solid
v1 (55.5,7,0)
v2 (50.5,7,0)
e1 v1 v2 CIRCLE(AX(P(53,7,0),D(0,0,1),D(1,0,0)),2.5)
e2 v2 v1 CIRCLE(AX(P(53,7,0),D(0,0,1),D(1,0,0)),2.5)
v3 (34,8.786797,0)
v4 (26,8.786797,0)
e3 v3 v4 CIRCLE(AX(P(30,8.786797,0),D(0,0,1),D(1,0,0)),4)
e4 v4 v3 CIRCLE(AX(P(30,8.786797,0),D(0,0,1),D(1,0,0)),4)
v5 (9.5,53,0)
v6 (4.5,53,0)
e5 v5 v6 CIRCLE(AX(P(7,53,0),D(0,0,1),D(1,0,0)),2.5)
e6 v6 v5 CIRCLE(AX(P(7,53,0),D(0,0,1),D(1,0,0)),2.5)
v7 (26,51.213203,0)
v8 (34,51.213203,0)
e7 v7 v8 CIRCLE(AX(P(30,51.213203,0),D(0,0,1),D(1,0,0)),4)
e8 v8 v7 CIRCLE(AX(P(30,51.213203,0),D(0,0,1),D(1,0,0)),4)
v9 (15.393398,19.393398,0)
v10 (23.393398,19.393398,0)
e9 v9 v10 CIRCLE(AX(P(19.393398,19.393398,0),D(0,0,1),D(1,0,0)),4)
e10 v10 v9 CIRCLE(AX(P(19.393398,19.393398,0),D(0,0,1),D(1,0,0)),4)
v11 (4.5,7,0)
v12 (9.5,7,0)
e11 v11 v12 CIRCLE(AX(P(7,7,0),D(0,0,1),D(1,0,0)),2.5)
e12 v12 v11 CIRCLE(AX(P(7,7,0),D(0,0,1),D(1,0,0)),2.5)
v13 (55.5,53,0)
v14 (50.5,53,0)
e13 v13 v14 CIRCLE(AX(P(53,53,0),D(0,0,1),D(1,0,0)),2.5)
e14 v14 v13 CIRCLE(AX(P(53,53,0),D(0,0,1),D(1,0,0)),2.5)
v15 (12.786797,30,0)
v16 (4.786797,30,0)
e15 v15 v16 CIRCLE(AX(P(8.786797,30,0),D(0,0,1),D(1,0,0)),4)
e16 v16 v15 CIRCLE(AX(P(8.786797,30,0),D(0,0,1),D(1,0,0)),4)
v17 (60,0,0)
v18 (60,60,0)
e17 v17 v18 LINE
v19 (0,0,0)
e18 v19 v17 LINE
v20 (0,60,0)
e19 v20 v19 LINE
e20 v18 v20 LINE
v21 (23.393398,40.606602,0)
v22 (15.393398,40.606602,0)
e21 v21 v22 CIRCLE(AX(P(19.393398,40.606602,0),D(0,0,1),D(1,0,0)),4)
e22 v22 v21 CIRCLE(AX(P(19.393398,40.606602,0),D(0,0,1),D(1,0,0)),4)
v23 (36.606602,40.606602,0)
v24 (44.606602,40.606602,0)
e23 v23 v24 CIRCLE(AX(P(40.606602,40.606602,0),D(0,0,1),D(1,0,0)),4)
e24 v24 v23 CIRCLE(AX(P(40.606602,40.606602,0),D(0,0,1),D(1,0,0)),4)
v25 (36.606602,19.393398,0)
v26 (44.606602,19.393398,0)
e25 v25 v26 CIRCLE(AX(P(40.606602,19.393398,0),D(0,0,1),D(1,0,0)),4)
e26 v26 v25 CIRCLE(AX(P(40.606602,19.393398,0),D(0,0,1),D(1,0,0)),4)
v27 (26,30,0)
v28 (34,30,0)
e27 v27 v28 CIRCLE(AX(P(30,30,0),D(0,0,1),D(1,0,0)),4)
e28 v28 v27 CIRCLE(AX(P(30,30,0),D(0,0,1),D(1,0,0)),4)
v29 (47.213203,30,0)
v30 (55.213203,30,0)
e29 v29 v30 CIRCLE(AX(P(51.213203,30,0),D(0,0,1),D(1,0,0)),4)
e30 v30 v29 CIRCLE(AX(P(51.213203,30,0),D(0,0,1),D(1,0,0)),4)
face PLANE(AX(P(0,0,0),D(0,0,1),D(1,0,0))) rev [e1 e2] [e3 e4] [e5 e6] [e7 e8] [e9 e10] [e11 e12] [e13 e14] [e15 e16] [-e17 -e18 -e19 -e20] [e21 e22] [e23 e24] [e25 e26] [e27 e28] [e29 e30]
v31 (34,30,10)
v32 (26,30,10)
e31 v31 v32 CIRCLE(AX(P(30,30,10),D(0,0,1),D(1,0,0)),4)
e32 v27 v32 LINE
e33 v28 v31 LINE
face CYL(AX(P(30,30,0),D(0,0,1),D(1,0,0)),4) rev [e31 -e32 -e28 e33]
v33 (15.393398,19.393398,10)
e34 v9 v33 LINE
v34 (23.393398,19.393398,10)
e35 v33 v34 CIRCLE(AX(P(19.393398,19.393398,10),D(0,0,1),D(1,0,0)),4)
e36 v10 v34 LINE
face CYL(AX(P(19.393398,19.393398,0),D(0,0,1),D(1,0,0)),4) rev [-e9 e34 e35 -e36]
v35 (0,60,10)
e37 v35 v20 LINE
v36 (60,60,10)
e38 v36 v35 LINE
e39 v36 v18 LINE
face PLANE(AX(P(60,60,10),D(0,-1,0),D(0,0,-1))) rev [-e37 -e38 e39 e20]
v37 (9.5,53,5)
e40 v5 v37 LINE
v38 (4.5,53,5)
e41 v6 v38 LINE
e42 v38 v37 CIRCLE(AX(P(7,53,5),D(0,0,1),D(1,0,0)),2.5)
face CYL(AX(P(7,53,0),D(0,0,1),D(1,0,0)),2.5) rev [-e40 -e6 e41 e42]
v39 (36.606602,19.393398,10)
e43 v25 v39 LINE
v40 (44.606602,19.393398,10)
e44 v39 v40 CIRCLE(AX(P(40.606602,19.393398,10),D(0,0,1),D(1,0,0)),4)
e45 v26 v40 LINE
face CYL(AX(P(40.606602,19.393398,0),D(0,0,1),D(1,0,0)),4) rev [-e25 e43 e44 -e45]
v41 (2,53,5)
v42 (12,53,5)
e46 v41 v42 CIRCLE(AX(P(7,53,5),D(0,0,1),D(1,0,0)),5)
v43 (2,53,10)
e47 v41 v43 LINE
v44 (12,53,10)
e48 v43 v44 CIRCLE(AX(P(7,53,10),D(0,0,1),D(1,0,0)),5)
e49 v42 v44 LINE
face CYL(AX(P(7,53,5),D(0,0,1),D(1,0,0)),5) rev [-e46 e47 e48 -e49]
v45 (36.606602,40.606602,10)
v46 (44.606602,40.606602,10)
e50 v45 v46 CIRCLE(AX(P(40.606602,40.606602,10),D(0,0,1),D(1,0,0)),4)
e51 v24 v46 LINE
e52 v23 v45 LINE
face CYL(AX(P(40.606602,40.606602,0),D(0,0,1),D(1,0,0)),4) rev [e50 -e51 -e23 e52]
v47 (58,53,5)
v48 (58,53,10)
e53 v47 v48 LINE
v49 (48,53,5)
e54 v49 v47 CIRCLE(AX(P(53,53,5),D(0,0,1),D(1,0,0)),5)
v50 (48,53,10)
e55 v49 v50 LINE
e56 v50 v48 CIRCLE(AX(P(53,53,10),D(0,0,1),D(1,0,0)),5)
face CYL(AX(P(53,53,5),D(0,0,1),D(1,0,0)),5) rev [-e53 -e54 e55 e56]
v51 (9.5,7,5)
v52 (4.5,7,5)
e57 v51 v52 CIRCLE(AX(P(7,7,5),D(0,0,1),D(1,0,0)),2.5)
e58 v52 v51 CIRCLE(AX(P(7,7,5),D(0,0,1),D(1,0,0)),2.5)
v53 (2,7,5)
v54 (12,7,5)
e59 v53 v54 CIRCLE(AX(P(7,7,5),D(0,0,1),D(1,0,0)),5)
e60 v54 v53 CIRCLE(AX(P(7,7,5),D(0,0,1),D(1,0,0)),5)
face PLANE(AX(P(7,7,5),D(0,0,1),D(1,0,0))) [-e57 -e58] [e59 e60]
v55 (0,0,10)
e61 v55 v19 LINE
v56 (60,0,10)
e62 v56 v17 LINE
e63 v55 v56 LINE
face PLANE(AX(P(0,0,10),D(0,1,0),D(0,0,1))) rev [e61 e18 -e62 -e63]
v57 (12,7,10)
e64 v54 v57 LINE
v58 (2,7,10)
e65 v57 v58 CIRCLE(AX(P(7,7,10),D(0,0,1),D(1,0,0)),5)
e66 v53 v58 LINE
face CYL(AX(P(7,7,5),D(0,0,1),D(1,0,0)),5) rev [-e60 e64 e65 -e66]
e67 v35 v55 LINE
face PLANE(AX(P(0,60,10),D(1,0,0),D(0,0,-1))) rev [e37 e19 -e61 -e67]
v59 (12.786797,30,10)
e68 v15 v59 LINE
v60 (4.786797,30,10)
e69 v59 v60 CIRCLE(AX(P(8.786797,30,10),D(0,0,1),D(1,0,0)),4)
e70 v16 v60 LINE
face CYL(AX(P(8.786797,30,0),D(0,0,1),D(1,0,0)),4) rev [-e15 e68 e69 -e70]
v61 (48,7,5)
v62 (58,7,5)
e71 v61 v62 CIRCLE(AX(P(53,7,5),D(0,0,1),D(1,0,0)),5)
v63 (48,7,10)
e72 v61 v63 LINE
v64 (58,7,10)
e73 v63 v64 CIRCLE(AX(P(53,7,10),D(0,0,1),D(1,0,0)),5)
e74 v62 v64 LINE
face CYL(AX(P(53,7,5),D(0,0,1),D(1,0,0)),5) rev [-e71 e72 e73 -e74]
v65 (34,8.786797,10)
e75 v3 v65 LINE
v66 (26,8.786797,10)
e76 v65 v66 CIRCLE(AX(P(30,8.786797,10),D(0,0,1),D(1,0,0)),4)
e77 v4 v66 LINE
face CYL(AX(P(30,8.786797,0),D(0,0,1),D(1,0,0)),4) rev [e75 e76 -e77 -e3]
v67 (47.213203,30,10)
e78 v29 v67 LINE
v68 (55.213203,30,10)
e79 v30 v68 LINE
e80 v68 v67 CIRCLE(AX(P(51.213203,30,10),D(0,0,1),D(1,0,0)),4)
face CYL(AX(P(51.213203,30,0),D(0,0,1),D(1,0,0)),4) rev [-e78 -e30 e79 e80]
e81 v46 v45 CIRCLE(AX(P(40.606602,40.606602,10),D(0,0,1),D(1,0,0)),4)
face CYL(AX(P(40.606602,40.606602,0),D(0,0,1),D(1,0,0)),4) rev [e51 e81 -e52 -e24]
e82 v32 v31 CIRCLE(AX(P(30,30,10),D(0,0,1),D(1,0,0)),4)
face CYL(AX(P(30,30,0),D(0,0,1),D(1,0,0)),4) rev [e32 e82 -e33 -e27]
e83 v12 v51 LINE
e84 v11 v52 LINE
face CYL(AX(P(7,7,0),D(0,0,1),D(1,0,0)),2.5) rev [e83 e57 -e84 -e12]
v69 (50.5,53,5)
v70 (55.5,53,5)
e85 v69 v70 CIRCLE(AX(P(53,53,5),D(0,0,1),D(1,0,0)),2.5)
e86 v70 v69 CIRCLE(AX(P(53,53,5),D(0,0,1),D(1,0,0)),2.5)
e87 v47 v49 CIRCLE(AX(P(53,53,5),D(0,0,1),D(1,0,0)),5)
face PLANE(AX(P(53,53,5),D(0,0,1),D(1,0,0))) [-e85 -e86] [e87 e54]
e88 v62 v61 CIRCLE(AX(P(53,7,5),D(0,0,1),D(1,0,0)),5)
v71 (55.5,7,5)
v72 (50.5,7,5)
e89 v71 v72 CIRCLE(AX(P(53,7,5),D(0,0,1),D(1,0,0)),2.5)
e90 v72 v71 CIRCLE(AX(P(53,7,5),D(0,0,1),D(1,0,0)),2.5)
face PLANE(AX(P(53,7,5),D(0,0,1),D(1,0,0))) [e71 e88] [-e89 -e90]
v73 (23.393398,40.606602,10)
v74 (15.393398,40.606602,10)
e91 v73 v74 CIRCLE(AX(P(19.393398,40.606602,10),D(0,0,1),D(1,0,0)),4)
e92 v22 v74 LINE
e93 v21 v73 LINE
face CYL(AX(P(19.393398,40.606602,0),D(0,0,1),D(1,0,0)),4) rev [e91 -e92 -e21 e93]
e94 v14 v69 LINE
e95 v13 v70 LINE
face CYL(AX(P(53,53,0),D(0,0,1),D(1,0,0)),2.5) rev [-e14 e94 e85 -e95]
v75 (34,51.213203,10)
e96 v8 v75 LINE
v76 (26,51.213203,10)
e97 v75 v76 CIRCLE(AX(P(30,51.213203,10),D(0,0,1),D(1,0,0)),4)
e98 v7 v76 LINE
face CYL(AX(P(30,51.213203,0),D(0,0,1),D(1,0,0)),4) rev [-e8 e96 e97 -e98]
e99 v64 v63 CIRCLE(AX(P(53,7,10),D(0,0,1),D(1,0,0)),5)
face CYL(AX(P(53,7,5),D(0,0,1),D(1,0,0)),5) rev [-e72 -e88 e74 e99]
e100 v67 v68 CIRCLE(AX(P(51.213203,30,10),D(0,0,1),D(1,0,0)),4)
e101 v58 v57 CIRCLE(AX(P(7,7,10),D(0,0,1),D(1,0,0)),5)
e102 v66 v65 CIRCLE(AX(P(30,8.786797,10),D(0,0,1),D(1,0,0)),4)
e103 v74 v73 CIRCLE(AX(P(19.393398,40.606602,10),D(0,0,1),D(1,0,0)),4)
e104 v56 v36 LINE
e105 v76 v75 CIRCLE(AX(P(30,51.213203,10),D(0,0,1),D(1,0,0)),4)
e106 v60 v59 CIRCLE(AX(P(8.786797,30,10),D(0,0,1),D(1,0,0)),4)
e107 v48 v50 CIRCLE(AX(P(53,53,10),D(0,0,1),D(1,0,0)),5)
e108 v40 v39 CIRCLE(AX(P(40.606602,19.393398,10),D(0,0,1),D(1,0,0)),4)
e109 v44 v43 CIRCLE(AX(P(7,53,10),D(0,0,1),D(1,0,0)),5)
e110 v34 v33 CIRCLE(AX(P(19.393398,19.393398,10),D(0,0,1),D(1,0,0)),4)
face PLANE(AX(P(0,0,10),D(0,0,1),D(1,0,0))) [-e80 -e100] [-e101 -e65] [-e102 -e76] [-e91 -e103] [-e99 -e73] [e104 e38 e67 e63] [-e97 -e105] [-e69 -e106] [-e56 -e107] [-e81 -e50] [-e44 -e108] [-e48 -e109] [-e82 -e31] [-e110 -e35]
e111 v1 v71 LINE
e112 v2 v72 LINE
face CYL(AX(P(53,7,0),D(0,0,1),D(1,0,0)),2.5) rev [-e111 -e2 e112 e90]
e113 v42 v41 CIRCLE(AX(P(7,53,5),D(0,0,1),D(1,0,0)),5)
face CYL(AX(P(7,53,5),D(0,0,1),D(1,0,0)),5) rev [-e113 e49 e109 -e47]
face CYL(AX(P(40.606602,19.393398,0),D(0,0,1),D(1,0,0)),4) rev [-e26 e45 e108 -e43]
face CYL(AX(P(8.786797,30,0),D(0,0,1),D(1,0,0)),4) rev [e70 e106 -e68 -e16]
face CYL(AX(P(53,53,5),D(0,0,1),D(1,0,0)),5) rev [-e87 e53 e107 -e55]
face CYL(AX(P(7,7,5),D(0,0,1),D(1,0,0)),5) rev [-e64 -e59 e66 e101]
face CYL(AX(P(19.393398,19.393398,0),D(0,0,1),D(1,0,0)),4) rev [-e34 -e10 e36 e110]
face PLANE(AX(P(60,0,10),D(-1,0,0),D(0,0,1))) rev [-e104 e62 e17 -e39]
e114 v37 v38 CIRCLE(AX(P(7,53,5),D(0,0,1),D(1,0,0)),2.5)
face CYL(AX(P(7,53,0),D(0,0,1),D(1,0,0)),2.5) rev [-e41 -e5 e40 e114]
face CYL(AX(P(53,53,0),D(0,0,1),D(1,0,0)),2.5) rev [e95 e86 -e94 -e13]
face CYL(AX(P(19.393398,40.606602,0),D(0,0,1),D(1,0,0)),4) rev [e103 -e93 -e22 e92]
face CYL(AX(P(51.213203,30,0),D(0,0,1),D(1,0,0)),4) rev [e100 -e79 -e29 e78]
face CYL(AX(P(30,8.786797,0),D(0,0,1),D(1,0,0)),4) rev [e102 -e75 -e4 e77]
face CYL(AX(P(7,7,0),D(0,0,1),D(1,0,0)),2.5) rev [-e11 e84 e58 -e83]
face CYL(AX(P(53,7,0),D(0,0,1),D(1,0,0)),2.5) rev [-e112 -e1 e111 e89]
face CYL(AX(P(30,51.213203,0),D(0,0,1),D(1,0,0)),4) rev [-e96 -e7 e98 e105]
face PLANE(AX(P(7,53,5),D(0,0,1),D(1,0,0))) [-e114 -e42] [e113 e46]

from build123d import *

# Parameters (mm, degrees)
PLATE_PROFILE_60X60_W           = 60
PLATE_PROFILE_60X60_H           = 60
BASE_PLATE_60X60X10_DEPTH       = 10
COUNTERBORE_PROFILE_4X_10_R     = 5
CORNER_COUNTERBORES_4X_10_DEPTH = 5
CORNER_HOLE_PROFILE_4X_5_R      = 2.5
CORNER_HOLES_4X_5_DEPTH         = 5
INNER_THROUGH_HOLES_12X_DEPTH   = 10


with BuildPart() as part:
    # Plate Profile 60x60 → Base Plate 60x60x10 (new body)
    with BuildSketch(Plane.XY):
        with Locations((30, 30)):
            Rectangle(PLATE_PROFILE_60X60_W, PLATE_PROFILE_60X60_H)
    extrude(amount=BASE_PLATE_60X60X10_DEPTH)

    # Counterbore Profile 4xØ10 → Corner Counterbores 4xØ10 (cut)
    with BuildSketch(Plane.XY.offset(10)):
        with Locations((7, 53)):
            Circle(COUNTERBORE_PROFILE_4X_10_R)
        with Locations((53, 53)):
            Circle(COUNTERBORE_PROFILE_4X_10_R)
        with Locations((7, 7)):
            Circle(COUNTERBORE_PROFILE_4X_10_R)
        with Locations((53, 7)):
            Circle(COUNTERBORE_PROFILE_4X_10_R)
    extrude(amount=-CORNER_COUNTERBORES_4X_10_DEPTH, mode=Mode.SUBTRACT)

    # Corner Hole Profile 4xØ5 → Corner Holes 4xØ5 (cut)
    with BuildSketch(Plane.XY.offset(5)):
        with Locations((7, 53)):
            Circle(CORNER_HOLE_PROFILE_4X_5_R)
        with Locations((53, 53)):
            Circle(CORNER_HOLE_PROFILE_4X_5_R)
        with Locations((7, 7)):
            Circle(CORNER_HOLE_PROFILE_4X_5_R)
        with Locations((53, 7)):
            Circle(CORNER_HOLE_PROFILE_4X_5_R)
    extrude(amount=-CORNER_HOLES_4X_5_DEPTH, mode=Mode.SUBTRACT)

    # Inner Hole Grid Profile → Inner Through Holes 12x (cut)
    with BuildSketch(Plane.XY.offset(10)):
        with BuildLine():
            Line((22.221825407, 37.778174593), (19.393398282, 40.606601718))
            Line((19.393398282, 40.606601718), (16.564971157, 43.435028843))
            ThreePointArc((16.564971157, 43.435028843), (16.564971157, 37.778174593), (22.221825407, 37.778174593))
        make_face()
        with BuildLine():
            ThreePointArc((22.221825407, 37.778174593), (23.088916412, 39.075867988), (23.393398282, 40.606601718))
            Line((23.393398282, 40.606601718), (19.393398282, 40.606601718))
            Line((19.393398282, 40.606601718), (22.221825407, 37.778174593))
        make_face()
        with BuildLine():
            Line((19.393398282, 40.606601718), (23.393398282, 40.606601718))
            ThreePointArc((23.393398282, 40.606601718), (20.924132012, 44.302119848), (16.564971157, 43.435028843))
            Line((16.564971157, 43.435028843), (19.393398282, 40.606601718))
        make_face()
        with BuildLine():
            Line((30, 51.213203436), (30, 55.213203436))
            ThreePointArc((30, 55.213203436), (26, 51.213203436), (30, 47.213203436))
            Line((30, 47.213203436), (30, 51.213203436))
        make_face()
        with BuildLine():
            ThreePointArc((34, 51.213203436), (32.828427125, 54.04163056), (30, 55.213203436))
            Line((30, 55.213203436), (30, 51.213203436))
            Line((30, 51.213203436), (32.828427125, 48.384776311))
            ThreePointArc((32.828427125, 48.384776311), (33.69551813, 49.682469706), (34, 51.213203436))
        make_face()
        with BuildLine():
            Line((32.828427125, 48.384776311), (30, 51.213203436))
            Line((30, 51.213203436), (30, 47.213203436))
            ThreePointArc((30, 47.213203436), (31.530733729, 47.517685306), (32.828427125, 48.384776311))
        make_face()
        with BuildLine():
            Line((40.606601718, 40.606601718), (37.778174593, 43.435028843))
            ThreePointArc((37.778174593, 43.435028843), (36.911083588, 42.137335447), (36.606601718, 40.606601718))
            Line((36.606601718, 40.606601718), (40.606601718, 40.606601718))
        make_face()
        with BuildLine():
            ThreePointArc((43.435028843, 43.435028843), (40.606601718, 44.606601718), (37.778174593, 43.435028843))
            Line((37.778174593, 43.435028843), (40.606601718, 40.606601718))
            Line((40.606601718, 40.606601718), (43.435028843, 43.435028843))
        make_face()
        with BuildLine():
            Line((43.435028843, 37.778174593), (40.606601718, 40.606601718))
            Line((40.606601718, 40.606601718), (37.778174593, 37.778174593))
            ThreePointArc((37.778174593, 37.778174593), (40.606601718, 36.606601718), (43.435028843, 37.778174593))
        make_face()
        with BuildLine():
            Line((43.435028843, 43.435028843), (40.606601718, 40.606601718))
            Line((40.606601718, 40.606601718), (43.435028843, 37.778174593))
            ThreePointArc((43.435028843, 37.778174593), (44.302119848, 39.075867988), (44.606601718, 40.606601718))
            ThreePointArc((44.606601718, 40.606601718), (44.302119848, 42.137335447), (43.435028843, 43.435028843))
        make_face()
        with BuildLine():
            Line((40.606601718, 40.606601718), (36.606601718, 40.606601718))
            ThreePointArc((36.606601718, 40.606601718), (36.911083588, 39.075867988), (37.778174593, 37.778174593))
            Line((37.778174593, 37.778174593), (40.606601718, 40.606601718))
        make_face()
        with BuildLine():
            ThreePointArc((55.213203436, 30), (52.743937165, 33.69551813), (48.384776311, 32.828427125))
            Line((48.384776311, 32.828427125), (51.213203436, 30))
            Line((51.213203436, 30), (55.213203436, 30))
        make_face()
        with BuildLine():
            Line((51.213203436, 30), (48.384776311, 32.828427125))
            ThreePointArc((48.384776311, 32.828427125), (47.517685306, 31.530733729), (47.213203436, 30))
            Line((47.213203436, 30), (51.213203436, 30))
        make_face()
        with BuildLine():
            Line((51.213203436, 30), (47.213203436, 30))
            ThreePointArc((47.213203436, 30), (51.213203436, 26), (55.213203436, 30))
            Line((55.213203436, 30), (51.213203436, 30))
        make_face()
        with BuildLine():
            Line((40.606601718, 19.393398282), (37.778174593, 22.221825407))
            ThreePointArc((37.778174593, 22.221825407), (36.911083588, 20.924132012), (36.606601718, 19.393398282))
            Line((36.606601718, 19.393398282), (40.606601718, 19.393398282))
        make_face()
        with BuildLine():
            Line((40.606601718, 19.393398282), (36.606601718, 19.393398282))
            ThreePointArc((36.606601718, 19.393398282), (39.075867988, 15.697880152), (43.435028843, 16.564971157))
            Line((43.435028843, 16.564971157), (40.606601718, 19.393398282))
        make_face()
        with BuildLine():
            ThreePointArc((44.606601718, 19.393398282), (42.137335447, 23.088916412), (37.778174593, 22.221825407))
            Line((37.778174593, 22.221825407), (40.606601718, 19.393398282))
            Line((40.606601718, 19.393398282), (43.435028843, 16.564971157))
            ThreePointArc((43.435028843, 16.564971157), (44.302119848, 17.862664553), (44.606601718, 19.393398282))
        make_face()
        with BuildLine():
            Line((22.221825407, 16.564971157), (19.393398282, 19.393398282))
            Line((19.393398282, 19.393398282), (16.564971157, 22.221825407))
            ThreePointArc((16.564971157, 22.221825407), (16.564971157, 16.564971157), (22.221825407, 16.564971157))
        make_face()
        with BuildLine():
            ThreePointArc((11.615223689, 27.171572875), (12.482314694, 28.469266271), (12.786796564, 30))
            Line((12.786796564, 30), (8.786796564, 30))
            Line((8.786796564, 30), (11.615223689, 27.171572875))
        make_face()
        with BuildLine():
            Line((11.615223689, 27.171572875), (8.786796564, 30))
            Line((8.786796564, 30), (4.786796564, 30))
            ThreePointArc((4.786796564, 30), (7.256062835, 26.30448187), (11.615223689, 27.171572875))
        make_face()
        with BuildLine():
            Line((8.786796564, 30), (12.786796564, 30))
            ThreePointArc((12.786796564, 30), (8.786796564, 34), (4.786796564, 30))
            Line((4.786796564, 30), (8.786796564, 30))
        make_face()
        with BuildLine():
            ThreePointArc((34, 8.786796564), (32.828427125, 11.615223689), (30, 12.786796564))
            Line((30, 12.786796564), (30, 8.786796564))
            Line((30, 8.786796564), (30, 4.786796564))
            ThreePointArc((30, 4.786796564), (32.828427125, 5.95836944), (34, 8.786796564))
        make_face()
        with BuildLine():
            Line((30, 8.786796564), (30, 12.786796564))
            ThreePointArc((30, 12.786796564), (28.469266271, 12.482314694), (27.171572875, 11.615223689))
            Line((27.171572875, 11.615223689), (30, 8.786796564))
        make_face()
        with BuildLine():
            Line((30, 4.786796564), (30, 8.786796564))
            Line((30, 8.786796564), (27.171572875, 11.615223689))
            ThreePointArc((27.171572875, 11.615223689), (26.30448187, 7.256062835), (30, 4.786796564))
        make_face()
        with BuildLine():
            Line((19.393398282, 19.393398282), (22.221825407, 22.221825407))
            ThreePointArc((22.221825407, 22.221825407), (19.393398282, 23.393398282), (16.564971157, 22.221825407))
            Line((16.564971157, 22.221825407), (19.393398282, 19.393398282))
        make_face()
        with BuildLine():
            ThreePointArc((23.393398282, 19.393398282), (23.088916412, 20.924132012), (22.221825407, 22.221825407))
            Line((22.221825407, 22.221825407), (19.393398282, 19.393398282))
            Line((19.393398282, 19.393398282), (23.393398282, 19.393398282))
        make_face()
        with BuildLine():
            ThreePointArc((22.221825407, 16.564971157), (23.088916412, 17.862664553), (23.393398282, 19.393398282))
            Line((23.393398282, 19.393398282), (19.393398282, 19.393398282))
            Line((19.393398282, 19.393398282), (22.221825407, 16.564971157))
        make_face()
        with BuildLine():
            Line((26, 30), (30, 30))
            Line((30, 30), (27.171572875, 32.828427125))
            ThreePointArc((27.171572875, 32.828427125), (26.30448187, 31.530733729), (26, 30))
        make_face()
        with BuildLine():
            Line((34, 30), (30, 30))
            Line((30, 30), (32.828427125, 27.171572875))
            ThreePointArc((32.828427125, 27.171572875), (33.69551813, 28.469266271), (34, 30))
        make_face()
        with BuildLine():
            Line((32.828427125, 32.828427125), (30, 30))
            Line((30, 30), (34, 30))
            ThreePointArc((34, 30), (33.69551813, 31.530733729), (32.828427125, 32.828427125))
        make_face()
        with BuildLine():
            ThreePointArc((32.828427125, 32.828427125), (31.530733729, 33.69551813), (30, 34))
            Line((30, 34), (30, 30))
            Line((30, 30), (32.828427125, 32.828427125))
        make_face()
        with BuildLine():
            Line((30, 30), (30, 34))
            ThreePointArc((30, 34), (28.469266271, 33.69551813), (27.171572875, 32.828427125))
            Line((27.171572875, 32.828427125), (30, 30))
        make_face()
        with BuildLine():
            Line((32.828427125, 27.171572875), (30, 30))
            Line((30, 30), (30, 26))
            ThreePointArc((30, 26), (31.530733729, 26.30448187), (32.828427125, 27.171572875))
        make_face()
        with BuildLine():
            Line((27.171572875, 27.171572875), (30, 30))
            Line((30, 30), (26, 30))
            ThreePointArc((26, 30), (26.30448187, 28.469266271), (27.171572875, 27.171572875))
        make_face()
        with BuildLine():
            Line((30, 26), (30, 30))
            Line((30, 30), (27.171572875, 27.171572875))
            ThreePointArc((27.171572875, 27.171572875), (28.469266271, 26.30448187), (30, 26))
        make_face()
    extrude(amount=-INNER_THROUGH_HOLES_12X_DEPTH, mode=Mode.SUBTRACT)


solid = part.part
